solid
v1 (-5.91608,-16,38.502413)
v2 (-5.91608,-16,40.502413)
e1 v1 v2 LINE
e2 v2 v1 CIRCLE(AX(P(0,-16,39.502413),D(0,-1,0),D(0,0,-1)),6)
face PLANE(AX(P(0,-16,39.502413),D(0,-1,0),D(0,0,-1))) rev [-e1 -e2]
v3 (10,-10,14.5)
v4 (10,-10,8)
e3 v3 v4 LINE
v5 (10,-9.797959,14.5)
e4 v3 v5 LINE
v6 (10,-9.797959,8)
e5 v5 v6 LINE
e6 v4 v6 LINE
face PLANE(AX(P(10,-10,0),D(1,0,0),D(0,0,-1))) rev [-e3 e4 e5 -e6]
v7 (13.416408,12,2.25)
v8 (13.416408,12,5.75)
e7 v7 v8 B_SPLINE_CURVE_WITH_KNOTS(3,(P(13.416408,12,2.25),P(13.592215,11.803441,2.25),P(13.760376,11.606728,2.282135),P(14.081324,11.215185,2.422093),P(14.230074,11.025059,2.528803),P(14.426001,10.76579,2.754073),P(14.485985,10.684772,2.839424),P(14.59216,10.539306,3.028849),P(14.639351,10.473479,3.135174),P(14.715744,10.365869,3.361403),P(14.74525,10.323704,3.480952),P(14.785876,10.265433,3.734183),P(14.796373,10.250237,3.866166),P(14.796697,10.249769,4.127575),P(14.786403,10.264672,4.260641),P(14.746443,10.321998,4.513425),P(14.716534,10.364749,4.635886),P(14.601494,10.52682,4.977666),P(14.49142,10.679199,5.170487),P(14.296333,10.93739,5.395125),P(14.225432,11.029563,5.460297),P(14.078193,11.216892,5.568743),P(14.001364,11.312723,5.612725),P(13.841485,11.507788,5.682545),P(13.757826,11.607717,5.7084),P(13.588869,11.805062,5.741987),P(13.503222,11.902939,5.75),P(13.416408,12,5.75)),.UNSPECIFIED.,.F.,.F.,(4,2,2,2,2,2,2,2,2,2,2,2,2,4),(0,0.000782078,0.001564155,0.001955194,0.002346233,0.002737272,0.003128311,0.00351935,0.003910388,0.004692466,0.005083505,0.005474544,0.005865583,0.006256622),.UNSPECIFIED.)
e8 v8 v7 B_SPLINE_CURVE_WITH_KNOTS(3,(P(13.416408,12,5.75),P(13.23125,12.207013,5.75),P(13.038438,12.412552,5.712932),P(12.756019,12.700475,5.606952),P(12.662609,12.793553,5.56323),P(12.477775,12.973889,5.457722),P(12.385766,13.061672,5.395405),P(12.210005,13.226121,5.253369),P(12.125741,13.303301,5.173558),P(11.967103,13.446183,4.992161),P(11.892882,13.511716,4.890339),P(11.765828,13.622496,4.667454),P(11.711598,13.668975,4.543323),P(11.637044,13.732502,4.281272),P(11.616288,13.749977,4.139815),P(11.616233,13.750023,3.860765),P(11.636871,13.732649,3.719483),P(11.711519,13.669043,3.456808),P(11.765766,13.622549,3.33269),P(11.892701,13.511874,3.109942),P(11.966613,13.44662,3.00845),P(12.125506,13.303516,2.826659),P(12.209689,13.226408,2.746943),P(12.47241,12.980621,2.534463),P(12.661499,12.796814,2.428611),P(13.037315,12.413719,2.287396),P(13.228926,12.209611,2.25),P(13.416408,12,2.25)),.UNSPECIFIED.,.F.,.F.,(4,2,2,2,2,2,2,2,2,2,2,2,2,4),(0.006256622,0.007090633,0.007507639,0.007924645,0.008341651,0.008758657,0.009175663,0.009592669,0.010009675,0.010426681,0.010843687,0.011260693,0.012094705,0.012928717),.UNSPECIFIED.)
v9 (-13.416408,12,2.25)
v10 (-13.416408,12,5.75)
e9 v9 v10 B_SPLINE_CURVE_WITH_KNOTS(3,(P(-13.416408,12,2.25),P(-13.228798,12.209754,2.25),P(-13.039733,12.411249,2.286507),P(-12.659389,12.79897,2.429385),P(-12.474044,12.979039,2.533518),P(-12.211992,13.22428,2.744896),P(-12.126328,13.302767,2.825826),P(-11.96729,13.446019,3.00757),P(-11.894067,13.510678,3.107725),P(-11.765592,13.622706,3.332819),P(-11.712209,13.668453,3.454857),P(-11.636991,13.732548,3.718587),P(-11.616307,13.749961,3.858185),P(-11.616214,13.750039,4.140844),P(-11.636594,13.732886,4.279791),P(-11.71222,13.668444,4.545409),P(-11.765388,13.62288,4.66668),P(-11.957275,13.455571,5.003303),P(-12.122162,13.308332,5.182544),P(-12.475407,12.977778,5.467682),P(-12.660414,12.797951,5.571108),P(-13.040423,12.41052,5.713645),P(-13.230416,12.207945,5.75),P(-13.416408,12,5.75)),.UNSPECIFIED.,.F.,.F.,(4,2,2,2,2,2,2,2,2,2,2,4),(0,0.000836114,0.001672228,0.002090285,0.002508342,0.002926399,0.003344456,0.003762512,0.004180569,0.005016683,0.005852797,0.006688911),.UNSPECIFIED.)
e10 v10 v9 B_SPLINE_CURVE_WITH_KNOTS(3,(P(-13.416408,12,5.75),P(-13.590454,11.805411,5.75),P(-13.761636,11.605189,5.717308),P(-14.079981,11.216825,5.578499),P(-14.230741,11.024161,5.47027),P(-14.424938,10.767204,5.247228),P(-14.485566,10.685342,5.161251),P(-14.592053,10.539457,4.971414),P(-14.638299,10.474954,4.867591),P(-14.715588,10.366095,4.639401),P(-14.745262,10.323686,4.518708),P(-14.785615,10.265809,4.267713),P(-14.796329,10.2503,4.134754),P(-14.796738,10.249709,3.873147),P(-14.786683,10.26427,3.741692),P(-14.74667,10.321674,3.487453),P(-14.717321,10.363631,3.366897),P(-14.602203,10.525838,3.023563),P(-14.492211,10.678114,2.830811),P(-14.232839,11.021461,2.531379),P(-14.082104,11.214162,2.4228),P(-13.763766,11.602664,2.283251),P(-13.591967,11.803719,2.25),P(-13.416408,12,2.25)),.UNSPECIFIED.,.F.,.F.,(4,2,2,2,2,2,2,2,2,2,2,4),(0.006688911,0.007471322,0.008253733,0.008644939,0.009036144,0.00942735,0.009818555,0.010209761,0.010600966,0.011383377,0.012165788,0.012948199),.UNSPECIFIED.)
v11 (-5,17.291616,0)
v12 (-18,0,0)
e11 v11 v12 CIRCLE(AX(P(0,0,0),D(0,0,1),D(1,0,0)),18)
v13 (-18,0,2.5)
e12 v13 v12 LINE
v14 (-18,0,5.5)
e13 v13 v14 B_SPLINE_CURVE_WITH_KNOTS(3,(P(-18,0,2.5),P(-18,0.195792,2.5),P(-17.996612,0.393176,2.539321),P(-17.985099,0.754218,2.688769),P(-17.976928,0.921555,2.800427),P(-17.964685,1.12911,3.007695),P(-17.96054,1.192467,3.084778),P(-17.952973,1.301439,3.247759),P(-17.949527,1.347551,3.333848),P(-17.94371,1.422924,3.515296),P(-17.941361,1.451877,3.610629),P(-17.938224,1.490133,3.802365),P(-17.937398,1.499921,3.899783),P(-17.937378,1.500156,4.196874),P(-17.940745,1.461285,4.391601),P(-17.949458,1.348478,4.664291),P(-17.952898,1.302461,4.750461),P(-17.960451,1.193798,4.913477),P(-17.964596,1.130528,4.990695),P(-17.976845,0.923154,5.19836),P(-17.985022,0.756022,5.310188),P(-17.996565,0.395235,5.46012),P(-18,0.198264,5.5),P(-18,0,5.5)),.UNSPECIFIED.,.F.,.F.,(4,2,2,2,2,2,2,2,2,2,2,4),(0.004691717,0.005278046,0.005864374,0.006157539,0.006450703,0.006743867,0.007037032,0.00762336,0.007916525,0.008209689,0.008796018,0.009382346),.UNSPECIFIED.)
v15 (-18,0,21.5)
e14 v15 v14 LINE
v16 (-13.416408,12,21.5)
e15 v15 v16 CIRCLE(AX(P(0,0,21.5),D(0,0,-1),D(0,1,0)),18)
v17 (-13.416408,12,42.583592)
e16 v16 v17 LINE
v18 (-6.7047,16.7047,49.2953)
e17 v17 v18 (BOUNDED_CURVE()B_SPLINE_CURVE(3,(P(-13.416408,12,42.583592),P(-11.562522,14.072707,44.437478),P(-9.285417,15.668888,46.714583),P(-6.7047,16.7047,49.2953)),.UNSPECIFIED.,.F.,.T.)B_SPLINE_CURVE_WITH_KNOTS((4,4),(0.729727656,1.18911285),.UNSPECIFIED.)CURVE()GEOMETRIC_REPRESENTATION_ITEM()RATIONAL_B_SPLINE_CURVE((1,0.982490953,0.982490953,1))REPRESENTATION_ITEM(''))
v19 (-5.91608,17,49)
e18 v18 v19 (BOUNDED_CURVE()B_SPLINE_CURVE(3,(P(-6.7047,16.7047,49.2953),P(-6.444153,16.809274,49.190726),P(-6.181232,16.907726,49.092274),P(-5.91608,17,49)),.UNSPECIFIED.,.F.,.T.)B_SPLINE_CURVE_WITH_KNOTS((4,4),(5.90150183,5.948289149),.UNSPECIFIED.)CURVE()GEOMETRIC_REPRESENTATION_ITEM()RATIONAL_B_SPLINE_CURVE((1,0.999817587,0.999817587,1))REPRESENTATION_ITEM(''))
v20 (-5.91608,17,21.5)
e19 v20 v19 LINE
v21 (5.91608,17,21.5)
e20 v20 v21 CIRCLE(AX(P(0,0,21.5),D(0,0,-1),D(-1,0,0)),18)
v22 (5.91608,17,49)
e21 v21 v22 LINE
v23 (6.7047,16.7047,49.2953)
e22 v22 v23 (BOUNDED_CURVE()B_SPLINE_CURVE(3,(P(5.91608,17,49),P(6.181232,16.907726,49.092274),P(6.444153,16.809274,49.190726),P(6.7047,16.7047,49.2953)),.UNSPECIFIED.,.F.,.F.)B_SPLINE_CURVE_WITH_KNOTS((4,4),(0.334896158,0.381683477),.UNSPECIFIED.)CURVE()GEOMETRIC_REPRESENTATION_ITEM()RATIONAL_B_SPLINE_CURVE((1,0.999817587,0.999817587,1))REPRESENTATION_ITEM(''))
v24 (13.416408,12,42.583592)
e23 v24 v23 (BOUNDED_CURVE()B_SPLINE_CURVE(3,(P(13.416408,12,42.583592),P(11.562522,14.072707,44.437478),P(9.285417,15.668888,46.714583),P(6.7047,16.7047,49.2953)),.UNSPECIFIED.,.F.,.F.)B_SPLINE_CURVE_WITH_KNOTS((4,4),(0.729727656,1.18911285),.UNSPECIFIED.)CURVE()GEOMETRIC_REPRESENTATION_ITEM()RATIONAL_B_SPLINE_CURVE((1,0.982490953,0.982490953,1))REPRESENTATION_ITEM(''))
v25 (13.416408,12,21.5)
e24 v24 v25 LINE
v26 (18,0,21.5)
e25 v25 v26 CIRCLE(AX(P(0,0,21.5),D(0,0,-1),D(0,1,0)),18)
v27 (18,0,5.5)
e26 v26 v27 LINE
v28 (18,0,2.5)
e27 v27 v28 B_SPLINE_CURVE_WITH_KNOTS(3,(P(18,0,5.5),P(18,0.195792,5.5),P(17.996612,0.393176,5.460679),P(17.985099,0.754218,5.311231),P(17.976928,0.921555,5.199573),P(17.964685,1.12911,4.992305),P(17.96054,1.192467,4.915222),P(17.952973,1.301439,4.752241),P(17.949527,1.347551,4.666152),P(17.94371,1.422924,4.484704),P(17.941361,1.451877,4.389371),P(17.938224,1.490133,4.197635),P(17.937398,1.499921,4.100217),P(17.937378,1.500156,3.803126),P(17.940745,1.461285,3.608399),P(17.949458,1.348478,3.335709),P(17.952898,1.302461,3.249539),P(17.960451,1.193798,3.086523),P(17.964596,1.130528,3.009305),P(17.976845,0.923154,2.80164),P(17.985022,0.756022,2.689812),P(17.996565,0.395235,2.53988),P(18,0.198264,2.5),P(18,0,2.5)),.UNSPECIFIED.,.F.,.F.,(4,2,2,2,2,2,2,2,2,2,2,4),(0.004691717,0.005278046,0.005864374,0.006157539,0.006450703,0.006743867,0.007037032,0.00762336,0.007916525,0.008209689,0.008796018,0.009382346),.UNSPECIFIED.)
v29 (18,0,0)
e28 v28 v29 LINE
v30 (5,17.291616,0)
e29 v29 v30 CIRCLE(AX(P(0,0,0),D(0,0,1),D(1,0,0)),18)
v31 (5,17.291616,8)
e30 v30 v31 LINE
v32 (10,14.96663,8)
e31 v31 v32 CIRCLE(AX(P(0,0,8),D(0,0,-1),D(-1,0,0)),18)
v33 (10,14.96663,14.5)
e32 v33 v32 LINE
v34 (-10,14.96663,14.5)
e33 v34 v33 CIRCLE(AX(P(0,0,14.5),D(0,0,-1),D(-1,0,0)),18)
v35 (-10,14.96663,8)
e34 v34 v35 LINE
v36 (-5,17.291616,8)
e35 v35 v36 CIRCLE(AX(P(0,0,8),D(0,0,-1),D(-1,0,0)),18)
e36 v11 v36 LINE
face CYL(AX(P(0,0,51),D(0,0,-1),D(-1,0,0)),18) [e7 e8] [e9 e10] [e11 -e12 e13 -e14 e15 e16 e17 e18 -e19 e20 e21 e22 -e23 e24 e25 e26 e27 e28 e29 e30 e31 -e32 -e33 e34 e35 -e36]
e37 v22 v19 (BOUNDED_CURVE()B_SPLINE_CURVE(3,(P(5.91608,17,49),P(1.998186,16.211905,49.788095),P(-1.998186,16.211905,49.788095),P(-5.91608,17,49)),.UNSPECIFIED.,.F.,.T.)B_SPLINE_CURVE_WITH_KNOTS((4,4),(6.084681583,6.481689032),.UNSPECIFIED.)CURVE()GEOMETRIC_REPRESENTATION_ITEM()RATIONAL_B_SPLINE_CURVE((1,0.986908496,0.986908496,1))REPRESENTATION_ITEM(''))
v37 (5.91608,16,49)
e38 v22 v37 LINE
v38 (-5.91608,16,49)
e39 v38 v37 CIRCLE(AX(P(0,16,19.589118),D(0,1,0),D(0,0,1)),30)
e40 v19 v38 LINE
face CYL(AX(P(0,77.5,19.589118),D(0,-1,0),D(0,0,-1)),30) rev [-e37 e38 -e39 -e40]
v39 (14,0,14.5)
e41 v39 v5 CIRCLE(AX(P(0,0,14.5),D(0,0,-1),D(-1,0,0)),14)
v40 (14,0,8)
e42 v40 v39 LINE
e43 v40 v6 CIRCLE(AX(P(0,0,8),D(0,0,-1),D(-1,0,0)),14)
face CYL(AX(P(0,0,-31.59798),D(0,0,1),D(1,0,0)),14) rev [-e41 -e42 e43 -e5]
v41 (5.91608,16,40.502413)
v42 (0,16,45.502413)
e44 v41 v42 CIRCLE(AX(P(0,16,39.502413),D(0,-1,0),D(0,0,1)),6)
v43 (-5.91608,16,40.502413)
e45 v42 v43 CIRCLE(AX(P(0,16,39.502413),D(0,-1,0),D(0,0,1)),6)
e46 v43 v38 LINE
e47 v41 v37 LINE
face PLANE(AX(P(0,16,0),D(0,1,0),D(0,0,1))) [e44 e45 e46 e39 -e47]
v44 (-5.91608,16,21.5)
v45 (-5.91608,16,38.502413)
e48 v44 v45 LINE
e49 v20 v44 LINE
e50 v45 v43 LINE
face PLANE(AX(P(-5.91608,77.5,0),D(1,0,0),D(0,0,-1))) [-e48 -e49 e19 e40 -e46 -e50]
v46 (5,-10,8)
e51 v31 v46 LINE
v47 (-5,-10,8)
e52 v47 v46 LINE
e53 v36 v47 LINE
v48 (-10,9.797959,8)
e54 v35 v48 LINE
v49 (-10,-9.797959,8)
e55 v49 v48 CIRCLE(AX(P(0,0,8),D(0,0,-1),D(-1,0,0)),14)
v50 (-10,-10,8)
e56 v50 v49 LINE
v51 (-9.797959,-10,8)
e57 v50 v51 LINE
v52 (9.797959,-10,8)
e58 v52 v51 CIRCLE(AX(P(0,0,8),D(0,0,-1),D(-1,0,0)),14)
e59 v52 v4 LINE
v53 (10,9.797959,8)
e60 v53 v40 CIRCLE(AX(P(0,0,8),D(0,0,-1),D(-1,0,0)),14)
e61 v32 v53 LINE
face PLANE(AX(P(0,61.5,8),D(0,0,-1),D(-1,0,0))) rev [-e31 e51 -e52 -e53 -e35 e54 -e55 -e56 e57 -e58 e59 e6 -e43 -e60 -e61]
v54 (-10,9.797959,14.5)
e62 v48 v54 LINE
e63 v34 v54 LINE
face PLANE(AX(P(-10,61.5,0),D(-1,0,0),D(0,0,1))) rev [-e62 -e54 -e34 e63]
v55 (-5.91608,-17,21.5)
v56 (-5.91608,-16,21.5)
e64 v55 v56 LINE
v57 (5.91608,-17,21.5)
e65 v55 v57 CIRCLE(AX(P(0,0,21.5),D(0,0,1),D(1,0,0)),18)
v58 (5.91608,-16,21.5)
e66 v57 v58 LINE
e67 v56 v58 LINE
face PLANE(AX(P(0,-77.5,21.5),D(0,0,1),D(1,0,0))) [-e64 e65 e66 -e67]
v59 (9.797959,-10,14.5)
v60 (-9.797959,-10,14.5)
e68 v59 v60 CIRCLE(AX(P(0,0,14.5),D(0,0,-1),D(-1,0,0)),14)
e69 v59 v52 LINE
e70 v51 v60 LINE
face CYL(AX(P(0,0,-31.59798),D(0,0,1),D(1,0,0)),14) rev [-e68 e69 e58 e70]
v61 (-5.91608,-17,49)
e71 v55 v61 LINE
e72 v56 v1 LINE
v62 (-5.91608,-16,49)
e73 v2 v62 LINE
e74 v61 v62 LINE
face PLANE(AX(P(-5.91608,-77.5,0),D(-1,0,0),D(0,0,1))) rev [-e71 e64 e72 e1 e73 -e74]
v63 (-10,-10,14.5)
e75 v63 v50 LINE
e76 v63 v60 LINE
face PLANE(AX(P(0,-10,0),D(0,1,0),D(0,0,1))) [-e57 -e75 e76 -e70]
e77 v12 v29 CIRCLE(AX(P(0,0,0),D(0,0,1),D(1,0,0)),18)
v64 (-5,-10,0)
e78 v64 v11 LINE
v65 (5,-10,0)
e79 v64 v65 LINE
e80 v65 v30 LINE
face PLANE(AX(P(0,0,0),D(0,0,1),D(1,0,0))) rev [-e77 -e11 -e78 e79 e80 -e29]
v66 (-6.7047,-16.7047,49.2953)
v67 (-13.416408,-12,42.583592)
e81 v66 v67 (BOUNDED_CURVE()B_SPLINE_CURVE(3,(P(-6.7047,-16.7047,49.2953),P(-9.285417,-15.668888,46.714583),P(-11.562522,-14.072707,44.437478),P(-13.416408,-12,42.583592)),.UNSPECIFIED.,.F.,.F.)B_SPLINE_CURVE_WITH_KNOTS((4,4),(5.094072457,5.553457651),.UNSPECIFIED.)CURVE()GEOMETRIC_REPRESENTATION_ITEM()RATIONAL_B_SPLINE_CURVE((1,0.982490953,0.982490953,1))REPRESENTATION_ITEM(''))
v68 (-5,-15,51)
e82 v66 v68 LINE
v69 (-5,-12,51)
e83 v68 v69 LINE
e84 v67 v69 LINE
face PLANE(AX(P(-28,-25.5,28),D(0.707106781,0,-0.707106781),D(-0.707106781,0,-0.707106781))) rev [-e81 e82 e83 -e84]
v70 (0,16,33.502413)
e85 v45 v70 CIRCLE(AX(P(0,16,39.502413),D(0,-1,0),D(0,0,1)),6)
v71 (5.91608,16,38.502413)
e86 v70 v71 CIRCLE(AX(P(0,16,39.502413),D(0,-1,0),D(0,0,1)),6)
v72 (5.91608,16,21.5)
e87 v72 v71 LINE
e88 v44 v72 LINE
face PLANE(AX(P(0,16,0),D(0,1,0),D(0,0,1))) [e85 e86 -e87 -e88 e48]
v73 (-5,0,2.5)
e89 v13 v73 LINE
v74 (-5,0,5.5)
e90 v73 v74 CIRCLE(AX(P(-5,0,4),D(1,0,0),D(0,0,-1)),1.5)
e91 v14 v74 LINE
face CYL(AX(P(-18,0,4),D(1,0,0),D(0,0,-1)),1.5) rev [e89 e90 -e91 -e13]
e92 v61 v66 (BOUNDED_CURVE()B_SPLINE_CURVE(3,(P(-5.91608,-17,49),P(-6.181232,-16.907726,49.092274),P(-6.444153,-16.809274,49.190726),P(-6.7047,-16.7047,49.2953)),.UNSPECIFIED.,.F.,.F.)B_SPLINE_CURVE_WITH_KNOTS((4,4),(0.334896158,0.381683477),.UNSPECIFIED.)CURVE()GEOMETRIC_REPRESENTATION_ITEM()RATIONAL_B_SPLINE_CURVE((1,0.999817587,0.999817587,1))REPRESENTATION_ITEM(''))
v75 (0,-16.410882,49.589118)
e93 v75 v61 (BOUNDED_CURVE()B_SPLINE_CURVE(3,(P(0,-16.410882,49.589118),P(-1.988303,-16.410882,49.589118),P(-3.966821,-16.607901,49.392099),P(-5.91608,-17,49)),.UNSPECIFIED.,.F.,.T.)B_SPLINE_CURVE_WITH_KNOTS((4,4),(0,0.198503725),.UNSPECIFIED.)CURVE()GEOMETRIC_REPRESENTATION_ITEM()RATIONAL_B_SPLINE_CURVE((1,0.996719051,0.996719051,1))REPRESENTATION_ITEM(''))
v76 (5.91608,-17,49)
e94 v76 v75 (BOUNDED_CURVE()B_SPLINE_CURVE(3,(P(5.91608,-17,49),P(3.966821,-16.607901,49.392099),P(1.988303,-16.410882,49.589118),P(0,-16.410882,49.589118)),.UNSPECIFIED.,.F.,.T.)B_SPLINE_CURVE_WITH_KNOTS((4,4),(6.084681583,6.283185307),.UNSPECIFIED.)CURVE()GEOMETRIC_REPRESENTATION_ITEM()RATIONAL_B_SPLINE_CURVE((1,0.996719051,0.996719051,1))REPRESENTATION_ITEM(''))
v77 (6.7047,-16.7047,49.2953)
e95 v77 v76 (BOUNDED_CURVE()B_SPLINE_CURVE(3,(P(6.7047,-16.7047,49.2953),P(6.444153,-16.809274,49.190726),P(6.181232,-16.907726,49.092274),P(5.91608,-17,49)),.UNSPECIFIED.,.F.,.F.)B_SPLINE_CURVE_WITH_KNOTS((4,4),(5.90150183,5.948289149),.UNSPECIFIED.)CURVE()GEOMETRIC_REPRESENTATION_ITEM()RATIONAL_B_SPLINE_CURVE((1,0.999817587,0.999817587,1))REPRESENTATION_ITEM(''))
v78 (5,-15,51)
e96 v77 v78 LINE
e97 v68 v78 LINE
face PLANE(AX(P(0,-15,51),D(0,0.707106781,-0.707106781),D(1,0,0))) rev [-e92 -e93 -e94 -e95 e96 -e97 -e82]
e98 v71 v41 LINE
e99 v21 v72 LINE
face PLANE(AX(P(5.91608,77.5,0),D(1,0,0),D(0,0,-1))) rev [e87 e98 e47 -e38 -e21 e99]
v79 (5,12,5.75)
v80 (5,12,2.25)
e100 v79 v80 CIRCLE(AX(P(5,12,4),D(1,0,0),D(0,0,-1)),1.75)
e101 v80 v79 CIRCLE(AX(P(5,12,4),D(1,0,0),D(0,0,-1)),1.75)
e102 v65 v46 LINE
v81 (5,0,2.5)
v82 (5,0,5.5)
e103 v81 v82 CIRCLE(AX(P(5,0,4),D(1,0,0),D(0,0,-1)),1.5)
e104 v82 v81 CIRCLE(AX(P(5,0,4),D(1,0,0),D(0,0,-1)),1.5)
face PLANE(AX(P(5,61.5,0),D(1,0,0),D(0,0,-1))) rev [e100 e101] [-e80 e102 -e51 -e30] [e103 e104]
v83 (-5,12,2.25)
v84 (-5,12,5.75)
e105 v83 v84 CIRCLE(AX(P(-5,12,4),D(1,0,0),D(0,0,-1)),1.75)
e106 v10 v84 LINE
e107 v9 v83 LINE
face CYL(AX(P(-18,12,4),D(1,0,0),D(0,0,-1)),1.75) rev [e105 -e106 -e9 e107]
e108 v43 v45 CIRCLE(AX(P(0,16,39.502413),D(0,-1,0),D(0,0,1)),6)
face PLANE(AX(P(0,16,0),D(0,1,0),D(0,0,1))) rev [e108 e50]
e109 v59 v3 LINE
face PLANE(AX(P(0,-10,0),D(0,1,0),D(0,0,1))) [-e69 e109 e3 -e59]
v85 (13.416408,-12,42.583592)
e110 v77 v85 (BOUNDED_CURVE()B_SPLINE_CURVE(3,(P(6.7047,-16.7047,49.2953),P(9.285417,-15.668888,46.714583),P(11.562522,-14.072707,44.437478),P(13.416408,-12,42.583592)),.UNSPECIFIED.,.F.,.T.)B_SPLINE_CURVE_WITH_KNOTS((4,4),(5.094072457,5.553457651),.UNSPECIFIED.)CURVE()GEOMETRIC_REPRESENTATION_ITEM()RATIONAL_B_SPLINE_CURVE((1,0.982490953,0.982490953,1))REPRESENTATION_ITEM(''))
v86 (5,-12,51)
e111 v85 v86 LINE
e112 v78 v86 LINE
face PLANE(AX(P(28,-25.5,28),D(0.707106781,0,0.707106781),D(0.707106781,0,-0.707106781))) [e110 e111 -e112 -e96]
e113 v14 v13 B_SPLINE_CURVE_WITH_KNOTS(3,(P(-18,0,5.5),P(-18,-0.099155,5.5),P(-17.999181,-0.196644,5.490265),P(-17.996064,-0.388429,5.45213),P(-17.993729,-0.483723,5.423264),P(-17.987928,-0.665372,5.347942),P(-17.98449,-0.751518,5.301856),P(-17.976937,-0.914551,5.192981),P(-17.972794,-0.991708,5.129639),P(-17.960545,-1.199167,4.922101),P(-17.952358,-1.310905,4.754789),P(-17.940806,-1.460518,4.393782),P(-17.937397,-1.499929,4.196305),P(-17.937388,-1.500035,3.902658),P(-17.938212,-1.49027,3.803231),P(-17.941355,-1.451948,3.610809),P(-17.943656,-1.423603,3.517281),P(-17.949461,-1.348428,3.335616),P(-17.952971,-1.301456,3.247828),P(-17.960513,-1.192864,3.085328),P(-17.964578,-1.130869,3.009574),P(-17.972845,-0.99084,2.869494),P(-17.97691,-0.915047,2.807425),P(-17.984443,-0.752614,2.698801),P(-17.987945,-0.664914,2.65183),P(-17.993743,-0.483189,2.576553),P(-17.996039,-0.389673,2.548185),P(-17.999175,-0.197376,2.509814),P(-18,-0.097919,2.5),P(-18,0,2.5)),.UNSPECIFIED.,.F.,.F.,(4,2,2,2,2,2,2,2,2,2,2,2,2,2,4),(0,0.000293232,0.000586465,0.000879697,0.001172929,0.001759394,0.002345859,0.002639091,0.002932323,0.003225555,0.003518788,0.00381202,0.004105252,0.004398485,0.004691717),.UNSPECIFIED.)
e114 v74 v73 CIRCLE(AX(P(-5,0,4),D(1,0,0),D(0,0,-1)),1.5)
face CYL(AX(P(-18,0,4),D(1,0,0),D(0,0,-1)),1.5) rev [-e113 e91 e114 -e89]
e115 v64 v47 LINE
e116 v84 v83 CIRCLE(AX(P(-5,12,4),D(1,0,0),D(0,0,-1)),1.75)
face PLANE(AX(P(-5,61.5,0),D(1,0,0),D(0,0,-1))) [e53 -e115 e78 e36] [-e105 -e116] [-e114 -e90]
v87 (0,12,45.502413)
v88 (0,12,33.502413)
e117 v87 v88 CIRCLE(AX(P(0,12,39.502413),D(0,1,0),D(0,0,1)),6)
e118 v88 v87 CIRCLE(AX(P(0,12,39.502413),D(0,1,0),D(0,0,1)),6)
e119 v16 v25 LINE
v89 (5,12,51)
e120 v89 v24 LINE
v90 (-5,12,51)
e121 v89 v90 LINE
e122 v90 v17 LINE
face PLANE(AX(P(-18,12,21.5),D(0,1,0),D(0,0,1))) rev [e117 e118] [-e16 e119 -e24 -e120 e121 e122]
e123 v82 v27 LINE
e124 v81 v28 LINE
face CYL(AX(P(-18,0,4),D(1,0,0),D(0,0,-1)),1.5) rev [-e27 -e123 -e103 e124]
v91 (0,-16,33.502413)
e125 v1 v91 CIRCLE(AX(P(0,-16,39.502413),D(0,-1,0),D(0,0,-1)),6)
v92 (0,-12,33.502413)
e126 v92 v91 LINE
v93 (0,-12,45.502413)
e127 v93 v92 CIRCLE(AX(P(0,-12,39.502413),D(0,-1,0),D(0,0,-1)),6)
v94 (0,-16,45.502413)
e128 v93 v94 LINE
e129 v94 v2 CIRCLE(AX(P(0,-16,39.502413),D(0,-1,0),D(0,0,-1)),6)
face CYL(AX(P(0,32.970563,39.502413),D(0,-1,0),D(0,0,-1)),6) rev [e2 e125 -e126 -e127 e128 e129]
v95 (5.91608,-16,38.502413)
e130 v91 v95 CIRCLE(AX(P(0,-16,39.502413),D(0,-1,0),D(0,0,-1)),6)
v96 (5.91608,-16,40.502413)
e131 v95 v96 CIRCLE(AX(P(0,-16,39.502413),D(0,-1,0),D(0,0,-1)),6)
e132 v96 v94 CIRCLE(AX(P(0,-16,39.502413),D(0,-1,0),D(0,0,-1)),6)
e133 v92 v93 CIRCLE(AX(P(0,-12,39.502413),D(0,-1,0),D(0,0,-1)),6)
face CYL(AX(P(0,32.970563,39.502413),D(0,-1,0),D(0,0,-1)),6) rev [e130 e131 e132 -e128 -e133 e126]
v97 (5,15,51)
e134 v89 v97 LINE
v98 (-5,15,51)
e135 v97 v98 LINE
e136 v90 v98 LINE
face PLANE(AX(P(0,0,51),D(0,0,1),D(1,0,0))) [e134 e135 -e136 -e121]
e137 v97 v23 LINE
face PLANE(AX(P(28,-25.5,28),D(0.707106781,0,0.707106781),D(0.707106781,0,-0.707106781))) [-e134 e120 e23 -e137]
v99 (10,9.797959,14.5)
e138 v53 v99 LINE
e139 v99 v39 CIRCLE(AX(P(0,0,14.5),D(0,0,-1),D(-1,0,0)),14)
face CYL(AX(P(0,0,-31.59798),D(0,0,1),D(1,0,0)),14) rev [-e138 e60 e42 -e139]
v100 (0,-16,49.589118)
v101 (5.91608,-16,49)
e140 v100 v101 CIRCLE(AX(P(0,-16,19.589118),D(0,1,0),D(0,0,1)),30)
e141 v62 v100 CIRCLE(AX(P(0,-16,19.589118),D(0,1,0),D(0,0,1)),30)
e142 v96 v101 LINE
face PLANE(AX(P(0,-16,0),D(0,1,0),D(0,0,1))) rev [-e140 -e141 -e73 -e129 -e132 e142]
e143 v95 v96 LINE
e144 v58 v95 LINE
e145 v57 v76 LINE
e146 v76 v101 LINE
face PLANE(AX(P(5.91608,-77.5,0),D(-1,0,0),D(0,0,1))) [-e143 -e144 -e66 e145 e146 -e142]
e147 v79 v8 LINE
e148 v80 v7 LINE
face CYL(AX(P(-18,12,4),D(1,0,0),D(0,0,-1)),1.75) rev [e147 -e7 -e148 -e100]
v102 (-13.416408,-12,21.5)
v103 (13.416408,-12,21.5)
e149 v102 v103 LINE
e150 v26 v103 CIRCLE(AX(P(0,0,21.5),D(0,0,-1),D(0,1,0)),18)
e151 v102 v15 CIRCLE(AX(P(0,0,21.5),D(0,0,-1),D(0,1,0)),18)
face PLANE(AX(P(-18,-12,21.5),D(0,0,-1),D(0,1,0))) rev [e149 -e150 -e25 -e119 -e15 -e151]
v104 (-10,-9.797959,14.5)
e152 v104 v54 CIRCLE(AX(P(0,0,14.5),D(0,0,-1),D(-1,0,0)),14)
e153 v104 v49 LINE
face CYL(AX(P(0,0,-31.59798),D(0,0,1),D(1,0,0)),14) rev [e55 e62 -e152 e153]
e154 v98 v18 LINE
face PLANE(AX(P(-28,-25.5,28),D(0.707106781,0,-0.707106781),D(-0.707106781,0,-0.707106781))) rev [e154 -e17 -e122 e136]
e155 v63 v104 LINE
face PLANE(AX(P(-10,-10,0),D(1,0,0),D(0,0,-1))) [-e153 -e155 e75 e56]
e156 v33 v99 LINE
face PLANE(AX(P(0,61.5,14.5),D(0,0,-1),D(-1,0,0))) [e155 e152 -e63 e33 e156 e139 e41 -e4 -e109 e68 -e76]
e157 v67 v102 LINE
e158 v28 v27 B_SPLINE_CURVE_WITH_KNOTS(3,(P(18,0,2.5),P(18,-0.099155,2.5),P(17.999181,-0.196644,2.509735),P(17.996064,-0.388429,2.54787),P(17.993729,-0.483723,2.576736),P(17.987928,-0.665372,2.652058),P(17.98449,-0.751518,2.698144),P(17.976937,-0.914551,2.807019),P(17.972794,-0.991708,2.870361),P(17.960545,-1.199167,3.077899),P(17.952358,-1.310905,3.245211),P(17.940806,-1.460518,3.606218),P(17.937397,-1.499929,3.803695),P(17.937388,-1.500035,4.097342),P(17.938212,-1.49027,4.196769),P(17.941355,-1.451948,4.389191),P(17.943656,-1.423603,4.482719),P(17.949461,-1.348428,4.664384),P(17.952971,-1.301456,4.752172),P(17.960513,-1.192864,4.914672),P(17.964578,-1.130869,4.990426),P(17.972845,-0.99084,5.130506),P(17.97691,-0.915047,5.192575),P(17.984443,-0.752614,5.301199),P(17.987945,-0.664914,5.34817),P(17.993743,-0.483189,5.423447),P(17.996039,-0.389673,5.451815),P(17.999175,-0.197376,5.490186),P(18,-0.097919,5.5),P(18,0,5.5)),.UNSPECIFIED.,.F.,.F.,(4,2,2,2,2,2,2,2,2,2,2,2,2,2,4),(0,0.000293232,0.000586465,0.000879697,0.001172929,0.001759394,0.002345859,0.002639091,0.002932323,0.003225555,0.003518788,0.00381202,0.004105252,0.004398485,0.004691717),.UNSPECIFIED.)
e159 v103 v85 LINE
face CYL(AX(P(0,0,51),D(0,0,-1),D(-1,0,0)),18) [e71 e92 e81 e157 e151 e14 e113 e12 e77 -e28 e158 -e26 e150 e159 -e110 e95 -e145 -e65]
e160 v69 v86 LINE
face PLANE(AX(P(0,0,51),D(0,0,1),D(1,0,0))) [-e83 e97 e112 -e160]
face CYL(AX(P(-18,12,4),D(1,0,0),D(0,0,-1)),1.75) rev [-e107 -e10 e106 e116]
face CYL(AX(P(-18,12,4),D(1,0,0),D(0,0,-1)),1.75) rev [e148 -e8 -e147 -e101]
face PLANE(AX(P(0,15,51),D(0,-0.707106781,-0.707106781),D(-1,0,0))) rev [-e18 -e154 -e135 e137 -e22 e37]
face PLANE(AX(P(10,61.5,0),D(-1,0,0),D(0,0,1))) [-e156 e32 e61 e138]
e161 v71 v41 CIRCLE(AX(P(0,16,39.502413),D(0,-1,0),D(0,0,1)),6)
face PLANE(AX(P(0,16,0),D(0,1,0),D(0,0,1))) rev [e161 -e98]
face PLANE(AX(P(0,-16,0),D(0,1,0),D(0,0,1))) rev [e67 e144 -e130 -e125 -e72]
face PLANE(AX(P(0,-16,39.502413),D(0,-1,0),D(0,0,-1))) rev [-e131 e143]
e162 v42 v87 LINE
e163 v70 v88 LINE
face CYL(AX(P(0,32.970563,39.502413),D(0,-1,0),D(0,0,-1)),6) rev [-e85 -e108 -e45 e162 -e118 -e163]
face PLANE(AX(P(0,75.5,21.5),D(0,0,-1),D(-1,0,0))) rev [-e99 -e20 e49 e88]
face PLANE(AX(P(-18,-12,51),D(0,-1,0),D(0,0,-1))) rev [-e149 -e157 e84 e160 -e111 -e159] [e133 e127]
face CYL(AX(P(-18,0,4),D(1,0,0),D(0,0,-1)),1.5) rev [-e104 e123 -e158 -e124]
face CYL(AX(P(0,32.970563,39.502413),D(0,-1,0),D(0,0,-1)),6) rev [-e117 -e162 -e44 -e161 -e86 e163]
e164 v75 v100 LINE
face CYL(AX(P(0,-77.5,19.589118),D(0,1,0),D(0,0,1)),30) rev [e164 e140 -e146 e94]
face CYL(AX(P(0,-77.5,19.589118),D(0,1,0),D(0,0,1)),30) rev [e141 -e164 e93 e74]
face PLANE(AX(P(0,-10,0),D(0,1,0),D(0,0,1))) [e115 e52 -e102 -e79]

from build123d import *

# Parameters (mm, degrees)
ROUND_BODY_SKETCH_36_R         = 18
ROUND_BODY_36X51_DEPTH         = 51
FORK_SLOT_12_WIDE_DEPTH        = 58
FORK_SLOT_12_WIDE_DEPTH_BACK   = 58
FORK_SLOT_SKETCH_W             = 29.5
FORK_SLOT_SKETCH_H             = 24
FORK_SIDE_FLATS_CUT_DEPTH      = 51
FORK_EDGE_CHAMFER_2X45_SIZE    = 2
FORK_PROFILE_TRIM_DEPTH        = 25.5
FORK_LUG_BOSS_DEPTH            = 27.5
FORK_START                     = 17
FORK_END_PROFILE_SKETCH_W      = 11.832159566
FORK_END_PROFILE_SKETCH_H      = 27.5
FORK_END_PROFILE_CUT_DEPTH     = 58.5
FORK_START_2                   = -16
SKETCH9_5_W                    = 11.832159566
SKETCH9_5_H                    = 27.5
FORK_LUG_CUT_A_DEPTH           = 61.5
FORK_START_3                   = 77.5
SKETCH9_6_W                    = 11.832159566
SKETCH9_6_H                    = 27.5
FORK_LUG_CUT_B_DEPTH           = 61.5
PIN_HOLE_12_REACH              = 65.883
PIN_HOLE_SKETCH_12_R           = 6
SHANK_PROFILE_SKETCH_W         = 20
SHANK_PROFILE_SKETCH_H         = 6.5
SHANK_PROFILE_SKETCH_W_2       = 10
SHANK_PROFILE_SKETCH_H_2       = 8
SHANK_PROFILE_CUT_DEPTH        = 61.5
SHANK_RELIEF_SKETCH_28_R       = 14
SHANK_RELIEF_28_DEPTH          = 6.5
CROSS_HOLES_DEPTH              = 59.77074102
CROSS_HOLES_DEPTH_BACK         = 59.77074102
CROSS_HOLES_SKETCH_R           = 1.75
CROSS_HOLES_SKETCH_R_2         = 1.5
SKETCH11_3_W                   = 10
SKETCH11_3_H                   = 8
SKETCH11_3_W_2                 = 20
SKETCH11_3_H_2                 = 6.5
SHANK_POCKET_CUT_10_DEEP_DEPTH = 10


with BuildPart() as part:
    # Round Body Sketch _36 → Round Body _36x51 (new body)
    with BuildSketch(Plane.XY):
        Circle(ROUND_BODY_SKETCH_36_R)
    extrude(amount=ROUND_BODY_36X51_DEPTH)

    # Fork Slot Sketch → Fork Slot 12 Wide (cut, two sides: drawn at the far end of the back side and taken through both)
    with BuildSketch(Plane(origin=(0, 0, 0), x_dir=(0, 0, -1), z_dir=(1, 0, 0)).offset(-FORK_SLOT_12_WIDE_DEPTH_BACK)):
        with Locations((-36.25, 0)):
            Rectangle(FORK_SLOT_SKETCH_W, FORK_SLOT_SKETCH_H)
    extrude(amount=FORK_SLOT_12_WIDE_DEPTH + FORK_SLOT_12_WIDE_DEPTH_BACK, mode=Mode.SUBTRACT)

    # Fork Flats Sketch → Fork Side Flats Cut (cut)
    with BuildSketch(Plane.XY.offset(21.5)):
        with BuildLine():
            Line((-5.916079783, 17), (5.916079783, 17))
            ThreePointArc((5.916079783, 17), (0, 18), (-5.916079783, 17))
        make_face()
        with BuildLine():
            Line((-5.916079783, -17), (5.916079783, -17))
            ThreePointArc((5.916079783, -17), (0, -18), (-5.916079783, -17))
        make_face()
    extrude(amount=FORK_SIDE_FLATS_CUT_DEPTH, mode=Mode.SUBTRACT)

    # Fork Edge Chamfer 2x45
    fork_edge_chamfer_2x45_edges = [part.edges().sort_by_distance(p)[0] for p in [
        (0, -17, 51),
        (0, 17, 51),
    ]]
    chamfer(fork_edge_chamfer_2x45_edges, length=FORK_EDGE_CHAMFER_2X45_SIZE)

    # Fork Profile Trim Sketch → Fork Profile Trim (cut, symmetric)
    with BuildSketch(Plane(origin=(0, 0, 0), x_dir=(1, 0, 0), z_dir=(0, 1, 0))):
        Polygon((-13.416407865, -51), (-5, -51), (-13.416407865, -42.583592135), align=None)
        Polygon((13.416407865, -42.583592135), (5, -51), (13.416407865, -51), align=None)
    extrude(amount=FORK_PROFILE_TRIM_DEPTH, both=True, mode=Mode.SUBTRACT)

    # Sketch5_2 → Fork Lug Boss (add)
    with BuildSketch(Plane.XY.offset(21.5)):
        with BuildLine():
            Line((-5.916079783, 17), (5.916079783, 17))
            ThreePointArc((5.916079783, 17), (0, 18), (-5.916079783, 17))
        make_face()
        with BuildLine():
            Line((-5.916079783, -17), (5.916079783, -17))
            ThreePointArc((5.916079783, -17), (0, -18), (-5.916079783, -17))
        make_face()
    extrude(amount=FORK_LUG_BOSS_DEPTH)

    # Fork End Profile Sketch → Fork End Profile Cut (cut)
    with BuildSketch(Plane(origin=(0, 0, 0), x_dir=(1, 0, 0), z_dir=(0, 1, 0)).offset(FORK_START)):
        with BuildLine():
            Line((-5.916079783, -49), (5.916079783, -49))
            ThreePointArc((5.916079783, -49), (0, -49.58911766), (-5.916079783, -49))
        make_face()
        with Locations((0, -35.25)):
            Rectangle(FORK_END_PROFILE_SKETCH_W, FORK_END_PROFILE_SKETCH_H)
    extrude(amount=FORK_END_PROFILE_CUT_DEPTH, mode=Mode.SUBTRACT)

    # Sketch9_5 → Fork Lug Cut A (cut)
    with BuildSketch(Plane(origin=(0, 0, 0), x_dir=(1, 0, 0), z_dir=(0, 1, 0)).offset(FORK_START_2)):
        with BuildLine():
            Line((-5.916079783, -49), (5.916079783, -49))
            ThreePointArc((5.916079783, -49), (0, -49.58911766), (-5.916079783, -49))
        make_face()
        with Locations((0, -35.25)):
            Rectangle(SKETCH9_5_W, SKETCH9_5_H)
    extrude(amount=-FORK_LUG_CUT_A_DEPTH, mode=Mode.SUBTRACT)

    # Sketch9_6 → Fork Lug Cut B (cut)
    with BuildSketch(Plane(origin=(0, 0, 0), x_dir=(1, 0, 0), z_dir=(0, 1, 0)).offset(FORK_START_3)):
        with BuildLine():
            Line((-5.916079783, -49), (5.916079783, -49))
            ThreePointArc((5.916079783, -49), (0, -49.58911766), (-5.916079783, -49))
        make_face()
        with Locations((0, -35.25)):
            Rectangle(SKETCH9_6_W, SKETCH9_6_H)
    extrude(amount=-FORK_LUG_CUT_B_DEPTH, mode=Mode.SUBTRACT)

    # Pin Hole _12: up to this face of the body (flat: up to its plane)
    pin_hole_12_end = Plane(part.part.faces().sort_by_distance((0, 16, 35.447312863))[0])
    # Pin Hole Sketch _12 → Pin Hole _12 (cut, up to the picked face)
    with BuildSketch(Plane.XZ.offset(16), mode=Mode.PRIVATE) as pin_hole_12_sk1:
        with Locations(Location((0, 39.502412714, 0), (0, 0, 270))):
            Circle(PIN_HOLE_SKETCH_12_R)
    pin_hole_12_tool1 = split(extrude(pin_hole_12_sk1.sketch, amount=-PIN_HOLE_12_REACH, mode=Mode.PRIVATE), bisect_by=pin_hole_12_end, keep=Keep.BOTH, mode=Mode.PRIVATE)
    add(pin_hole_12_tool1.solids().sort_by(Axis((0, -16, 39.502413), (0, 1, 0)))[0], mode=Mode.SUBTRACT)

    # Shank Profile Sketch → Shank Profile Cut (cut)
    with BuildSketch(Plane(origin=(0, 0, 0), x_dir=(1, 0, 0), z_dir=(0, 1, 0))):
        with Locations((0, -11.25)):
            Rectangle(SHANK_PROFILE_SKETCH_W, SHANK_PROFILE_SKETCH_H)
        with Locations((0, -4)):
            Rectangle(SHANK_PROFILE_SKETCH_W_2, SHANK_PROFILE_SKETCH_H_2)
    extrude(amount=SHANK_PROFILE_CUT_DEPTH, mode=Mode.SUBTRACT)

    # Shank Relief Sketch _28 → Shank Relief _28 (cut)
    with BuildSketch(Plane(origin=(0, 0, 14.5), x_dir=(-1, 0, 0), z_dir=(0, 0, -1))):
        Circle(SHANK_RELIEF_SKETCH_28_R)
    extrude(amount=SHANK_RELIEF_28_DEPTH, mode=Mode.SUBTRACT)

    # Cross Holes Sketch → Cross Holes (cut, two sides: drawn at the far end of the back side and taken through both)
    with BuildSketch(Plane(origin=(-5, 0, 0), x_dir=(0, 0, -1), z_dir=(1, 0, 0)).offset(-CROSS_HOLES_DEPTH_BACK)):
        with Locations((-4, 12)):
            Circle(CROSS_HOLES_SKETCH_R)
        with Locations((-4, 0)):
            Circle(CROSS_HOLES_SKETCH_R_2)
    extrude(amount=CROSS_HOLES_DEPTH + CROSS_HOLES_DEPTH_BACK, mode=Mode.SUBTRACT)

    # Sketch11_3 → Shank Pocket Cut 10 Deep (cut)
    with BuildSketch(Plane(origin=(0, 0, 0), x_dir=(1, 0, 0), z_dir=(0, 1, 0))):
        with Locations((0, -4)):
            Rectangle(SKETCH11_3_W, SKETCH11_3_H)
        with Locations((0, -11.25)):
            Rectangle(SKETCH11_3_W_2, SKETCH11_3_H_2)
    extrude(amount=-SHANK_POCKET_CUT_10_DEEP_DEPTH, mode=Mode.SUBTRACT)


solid = part.part
